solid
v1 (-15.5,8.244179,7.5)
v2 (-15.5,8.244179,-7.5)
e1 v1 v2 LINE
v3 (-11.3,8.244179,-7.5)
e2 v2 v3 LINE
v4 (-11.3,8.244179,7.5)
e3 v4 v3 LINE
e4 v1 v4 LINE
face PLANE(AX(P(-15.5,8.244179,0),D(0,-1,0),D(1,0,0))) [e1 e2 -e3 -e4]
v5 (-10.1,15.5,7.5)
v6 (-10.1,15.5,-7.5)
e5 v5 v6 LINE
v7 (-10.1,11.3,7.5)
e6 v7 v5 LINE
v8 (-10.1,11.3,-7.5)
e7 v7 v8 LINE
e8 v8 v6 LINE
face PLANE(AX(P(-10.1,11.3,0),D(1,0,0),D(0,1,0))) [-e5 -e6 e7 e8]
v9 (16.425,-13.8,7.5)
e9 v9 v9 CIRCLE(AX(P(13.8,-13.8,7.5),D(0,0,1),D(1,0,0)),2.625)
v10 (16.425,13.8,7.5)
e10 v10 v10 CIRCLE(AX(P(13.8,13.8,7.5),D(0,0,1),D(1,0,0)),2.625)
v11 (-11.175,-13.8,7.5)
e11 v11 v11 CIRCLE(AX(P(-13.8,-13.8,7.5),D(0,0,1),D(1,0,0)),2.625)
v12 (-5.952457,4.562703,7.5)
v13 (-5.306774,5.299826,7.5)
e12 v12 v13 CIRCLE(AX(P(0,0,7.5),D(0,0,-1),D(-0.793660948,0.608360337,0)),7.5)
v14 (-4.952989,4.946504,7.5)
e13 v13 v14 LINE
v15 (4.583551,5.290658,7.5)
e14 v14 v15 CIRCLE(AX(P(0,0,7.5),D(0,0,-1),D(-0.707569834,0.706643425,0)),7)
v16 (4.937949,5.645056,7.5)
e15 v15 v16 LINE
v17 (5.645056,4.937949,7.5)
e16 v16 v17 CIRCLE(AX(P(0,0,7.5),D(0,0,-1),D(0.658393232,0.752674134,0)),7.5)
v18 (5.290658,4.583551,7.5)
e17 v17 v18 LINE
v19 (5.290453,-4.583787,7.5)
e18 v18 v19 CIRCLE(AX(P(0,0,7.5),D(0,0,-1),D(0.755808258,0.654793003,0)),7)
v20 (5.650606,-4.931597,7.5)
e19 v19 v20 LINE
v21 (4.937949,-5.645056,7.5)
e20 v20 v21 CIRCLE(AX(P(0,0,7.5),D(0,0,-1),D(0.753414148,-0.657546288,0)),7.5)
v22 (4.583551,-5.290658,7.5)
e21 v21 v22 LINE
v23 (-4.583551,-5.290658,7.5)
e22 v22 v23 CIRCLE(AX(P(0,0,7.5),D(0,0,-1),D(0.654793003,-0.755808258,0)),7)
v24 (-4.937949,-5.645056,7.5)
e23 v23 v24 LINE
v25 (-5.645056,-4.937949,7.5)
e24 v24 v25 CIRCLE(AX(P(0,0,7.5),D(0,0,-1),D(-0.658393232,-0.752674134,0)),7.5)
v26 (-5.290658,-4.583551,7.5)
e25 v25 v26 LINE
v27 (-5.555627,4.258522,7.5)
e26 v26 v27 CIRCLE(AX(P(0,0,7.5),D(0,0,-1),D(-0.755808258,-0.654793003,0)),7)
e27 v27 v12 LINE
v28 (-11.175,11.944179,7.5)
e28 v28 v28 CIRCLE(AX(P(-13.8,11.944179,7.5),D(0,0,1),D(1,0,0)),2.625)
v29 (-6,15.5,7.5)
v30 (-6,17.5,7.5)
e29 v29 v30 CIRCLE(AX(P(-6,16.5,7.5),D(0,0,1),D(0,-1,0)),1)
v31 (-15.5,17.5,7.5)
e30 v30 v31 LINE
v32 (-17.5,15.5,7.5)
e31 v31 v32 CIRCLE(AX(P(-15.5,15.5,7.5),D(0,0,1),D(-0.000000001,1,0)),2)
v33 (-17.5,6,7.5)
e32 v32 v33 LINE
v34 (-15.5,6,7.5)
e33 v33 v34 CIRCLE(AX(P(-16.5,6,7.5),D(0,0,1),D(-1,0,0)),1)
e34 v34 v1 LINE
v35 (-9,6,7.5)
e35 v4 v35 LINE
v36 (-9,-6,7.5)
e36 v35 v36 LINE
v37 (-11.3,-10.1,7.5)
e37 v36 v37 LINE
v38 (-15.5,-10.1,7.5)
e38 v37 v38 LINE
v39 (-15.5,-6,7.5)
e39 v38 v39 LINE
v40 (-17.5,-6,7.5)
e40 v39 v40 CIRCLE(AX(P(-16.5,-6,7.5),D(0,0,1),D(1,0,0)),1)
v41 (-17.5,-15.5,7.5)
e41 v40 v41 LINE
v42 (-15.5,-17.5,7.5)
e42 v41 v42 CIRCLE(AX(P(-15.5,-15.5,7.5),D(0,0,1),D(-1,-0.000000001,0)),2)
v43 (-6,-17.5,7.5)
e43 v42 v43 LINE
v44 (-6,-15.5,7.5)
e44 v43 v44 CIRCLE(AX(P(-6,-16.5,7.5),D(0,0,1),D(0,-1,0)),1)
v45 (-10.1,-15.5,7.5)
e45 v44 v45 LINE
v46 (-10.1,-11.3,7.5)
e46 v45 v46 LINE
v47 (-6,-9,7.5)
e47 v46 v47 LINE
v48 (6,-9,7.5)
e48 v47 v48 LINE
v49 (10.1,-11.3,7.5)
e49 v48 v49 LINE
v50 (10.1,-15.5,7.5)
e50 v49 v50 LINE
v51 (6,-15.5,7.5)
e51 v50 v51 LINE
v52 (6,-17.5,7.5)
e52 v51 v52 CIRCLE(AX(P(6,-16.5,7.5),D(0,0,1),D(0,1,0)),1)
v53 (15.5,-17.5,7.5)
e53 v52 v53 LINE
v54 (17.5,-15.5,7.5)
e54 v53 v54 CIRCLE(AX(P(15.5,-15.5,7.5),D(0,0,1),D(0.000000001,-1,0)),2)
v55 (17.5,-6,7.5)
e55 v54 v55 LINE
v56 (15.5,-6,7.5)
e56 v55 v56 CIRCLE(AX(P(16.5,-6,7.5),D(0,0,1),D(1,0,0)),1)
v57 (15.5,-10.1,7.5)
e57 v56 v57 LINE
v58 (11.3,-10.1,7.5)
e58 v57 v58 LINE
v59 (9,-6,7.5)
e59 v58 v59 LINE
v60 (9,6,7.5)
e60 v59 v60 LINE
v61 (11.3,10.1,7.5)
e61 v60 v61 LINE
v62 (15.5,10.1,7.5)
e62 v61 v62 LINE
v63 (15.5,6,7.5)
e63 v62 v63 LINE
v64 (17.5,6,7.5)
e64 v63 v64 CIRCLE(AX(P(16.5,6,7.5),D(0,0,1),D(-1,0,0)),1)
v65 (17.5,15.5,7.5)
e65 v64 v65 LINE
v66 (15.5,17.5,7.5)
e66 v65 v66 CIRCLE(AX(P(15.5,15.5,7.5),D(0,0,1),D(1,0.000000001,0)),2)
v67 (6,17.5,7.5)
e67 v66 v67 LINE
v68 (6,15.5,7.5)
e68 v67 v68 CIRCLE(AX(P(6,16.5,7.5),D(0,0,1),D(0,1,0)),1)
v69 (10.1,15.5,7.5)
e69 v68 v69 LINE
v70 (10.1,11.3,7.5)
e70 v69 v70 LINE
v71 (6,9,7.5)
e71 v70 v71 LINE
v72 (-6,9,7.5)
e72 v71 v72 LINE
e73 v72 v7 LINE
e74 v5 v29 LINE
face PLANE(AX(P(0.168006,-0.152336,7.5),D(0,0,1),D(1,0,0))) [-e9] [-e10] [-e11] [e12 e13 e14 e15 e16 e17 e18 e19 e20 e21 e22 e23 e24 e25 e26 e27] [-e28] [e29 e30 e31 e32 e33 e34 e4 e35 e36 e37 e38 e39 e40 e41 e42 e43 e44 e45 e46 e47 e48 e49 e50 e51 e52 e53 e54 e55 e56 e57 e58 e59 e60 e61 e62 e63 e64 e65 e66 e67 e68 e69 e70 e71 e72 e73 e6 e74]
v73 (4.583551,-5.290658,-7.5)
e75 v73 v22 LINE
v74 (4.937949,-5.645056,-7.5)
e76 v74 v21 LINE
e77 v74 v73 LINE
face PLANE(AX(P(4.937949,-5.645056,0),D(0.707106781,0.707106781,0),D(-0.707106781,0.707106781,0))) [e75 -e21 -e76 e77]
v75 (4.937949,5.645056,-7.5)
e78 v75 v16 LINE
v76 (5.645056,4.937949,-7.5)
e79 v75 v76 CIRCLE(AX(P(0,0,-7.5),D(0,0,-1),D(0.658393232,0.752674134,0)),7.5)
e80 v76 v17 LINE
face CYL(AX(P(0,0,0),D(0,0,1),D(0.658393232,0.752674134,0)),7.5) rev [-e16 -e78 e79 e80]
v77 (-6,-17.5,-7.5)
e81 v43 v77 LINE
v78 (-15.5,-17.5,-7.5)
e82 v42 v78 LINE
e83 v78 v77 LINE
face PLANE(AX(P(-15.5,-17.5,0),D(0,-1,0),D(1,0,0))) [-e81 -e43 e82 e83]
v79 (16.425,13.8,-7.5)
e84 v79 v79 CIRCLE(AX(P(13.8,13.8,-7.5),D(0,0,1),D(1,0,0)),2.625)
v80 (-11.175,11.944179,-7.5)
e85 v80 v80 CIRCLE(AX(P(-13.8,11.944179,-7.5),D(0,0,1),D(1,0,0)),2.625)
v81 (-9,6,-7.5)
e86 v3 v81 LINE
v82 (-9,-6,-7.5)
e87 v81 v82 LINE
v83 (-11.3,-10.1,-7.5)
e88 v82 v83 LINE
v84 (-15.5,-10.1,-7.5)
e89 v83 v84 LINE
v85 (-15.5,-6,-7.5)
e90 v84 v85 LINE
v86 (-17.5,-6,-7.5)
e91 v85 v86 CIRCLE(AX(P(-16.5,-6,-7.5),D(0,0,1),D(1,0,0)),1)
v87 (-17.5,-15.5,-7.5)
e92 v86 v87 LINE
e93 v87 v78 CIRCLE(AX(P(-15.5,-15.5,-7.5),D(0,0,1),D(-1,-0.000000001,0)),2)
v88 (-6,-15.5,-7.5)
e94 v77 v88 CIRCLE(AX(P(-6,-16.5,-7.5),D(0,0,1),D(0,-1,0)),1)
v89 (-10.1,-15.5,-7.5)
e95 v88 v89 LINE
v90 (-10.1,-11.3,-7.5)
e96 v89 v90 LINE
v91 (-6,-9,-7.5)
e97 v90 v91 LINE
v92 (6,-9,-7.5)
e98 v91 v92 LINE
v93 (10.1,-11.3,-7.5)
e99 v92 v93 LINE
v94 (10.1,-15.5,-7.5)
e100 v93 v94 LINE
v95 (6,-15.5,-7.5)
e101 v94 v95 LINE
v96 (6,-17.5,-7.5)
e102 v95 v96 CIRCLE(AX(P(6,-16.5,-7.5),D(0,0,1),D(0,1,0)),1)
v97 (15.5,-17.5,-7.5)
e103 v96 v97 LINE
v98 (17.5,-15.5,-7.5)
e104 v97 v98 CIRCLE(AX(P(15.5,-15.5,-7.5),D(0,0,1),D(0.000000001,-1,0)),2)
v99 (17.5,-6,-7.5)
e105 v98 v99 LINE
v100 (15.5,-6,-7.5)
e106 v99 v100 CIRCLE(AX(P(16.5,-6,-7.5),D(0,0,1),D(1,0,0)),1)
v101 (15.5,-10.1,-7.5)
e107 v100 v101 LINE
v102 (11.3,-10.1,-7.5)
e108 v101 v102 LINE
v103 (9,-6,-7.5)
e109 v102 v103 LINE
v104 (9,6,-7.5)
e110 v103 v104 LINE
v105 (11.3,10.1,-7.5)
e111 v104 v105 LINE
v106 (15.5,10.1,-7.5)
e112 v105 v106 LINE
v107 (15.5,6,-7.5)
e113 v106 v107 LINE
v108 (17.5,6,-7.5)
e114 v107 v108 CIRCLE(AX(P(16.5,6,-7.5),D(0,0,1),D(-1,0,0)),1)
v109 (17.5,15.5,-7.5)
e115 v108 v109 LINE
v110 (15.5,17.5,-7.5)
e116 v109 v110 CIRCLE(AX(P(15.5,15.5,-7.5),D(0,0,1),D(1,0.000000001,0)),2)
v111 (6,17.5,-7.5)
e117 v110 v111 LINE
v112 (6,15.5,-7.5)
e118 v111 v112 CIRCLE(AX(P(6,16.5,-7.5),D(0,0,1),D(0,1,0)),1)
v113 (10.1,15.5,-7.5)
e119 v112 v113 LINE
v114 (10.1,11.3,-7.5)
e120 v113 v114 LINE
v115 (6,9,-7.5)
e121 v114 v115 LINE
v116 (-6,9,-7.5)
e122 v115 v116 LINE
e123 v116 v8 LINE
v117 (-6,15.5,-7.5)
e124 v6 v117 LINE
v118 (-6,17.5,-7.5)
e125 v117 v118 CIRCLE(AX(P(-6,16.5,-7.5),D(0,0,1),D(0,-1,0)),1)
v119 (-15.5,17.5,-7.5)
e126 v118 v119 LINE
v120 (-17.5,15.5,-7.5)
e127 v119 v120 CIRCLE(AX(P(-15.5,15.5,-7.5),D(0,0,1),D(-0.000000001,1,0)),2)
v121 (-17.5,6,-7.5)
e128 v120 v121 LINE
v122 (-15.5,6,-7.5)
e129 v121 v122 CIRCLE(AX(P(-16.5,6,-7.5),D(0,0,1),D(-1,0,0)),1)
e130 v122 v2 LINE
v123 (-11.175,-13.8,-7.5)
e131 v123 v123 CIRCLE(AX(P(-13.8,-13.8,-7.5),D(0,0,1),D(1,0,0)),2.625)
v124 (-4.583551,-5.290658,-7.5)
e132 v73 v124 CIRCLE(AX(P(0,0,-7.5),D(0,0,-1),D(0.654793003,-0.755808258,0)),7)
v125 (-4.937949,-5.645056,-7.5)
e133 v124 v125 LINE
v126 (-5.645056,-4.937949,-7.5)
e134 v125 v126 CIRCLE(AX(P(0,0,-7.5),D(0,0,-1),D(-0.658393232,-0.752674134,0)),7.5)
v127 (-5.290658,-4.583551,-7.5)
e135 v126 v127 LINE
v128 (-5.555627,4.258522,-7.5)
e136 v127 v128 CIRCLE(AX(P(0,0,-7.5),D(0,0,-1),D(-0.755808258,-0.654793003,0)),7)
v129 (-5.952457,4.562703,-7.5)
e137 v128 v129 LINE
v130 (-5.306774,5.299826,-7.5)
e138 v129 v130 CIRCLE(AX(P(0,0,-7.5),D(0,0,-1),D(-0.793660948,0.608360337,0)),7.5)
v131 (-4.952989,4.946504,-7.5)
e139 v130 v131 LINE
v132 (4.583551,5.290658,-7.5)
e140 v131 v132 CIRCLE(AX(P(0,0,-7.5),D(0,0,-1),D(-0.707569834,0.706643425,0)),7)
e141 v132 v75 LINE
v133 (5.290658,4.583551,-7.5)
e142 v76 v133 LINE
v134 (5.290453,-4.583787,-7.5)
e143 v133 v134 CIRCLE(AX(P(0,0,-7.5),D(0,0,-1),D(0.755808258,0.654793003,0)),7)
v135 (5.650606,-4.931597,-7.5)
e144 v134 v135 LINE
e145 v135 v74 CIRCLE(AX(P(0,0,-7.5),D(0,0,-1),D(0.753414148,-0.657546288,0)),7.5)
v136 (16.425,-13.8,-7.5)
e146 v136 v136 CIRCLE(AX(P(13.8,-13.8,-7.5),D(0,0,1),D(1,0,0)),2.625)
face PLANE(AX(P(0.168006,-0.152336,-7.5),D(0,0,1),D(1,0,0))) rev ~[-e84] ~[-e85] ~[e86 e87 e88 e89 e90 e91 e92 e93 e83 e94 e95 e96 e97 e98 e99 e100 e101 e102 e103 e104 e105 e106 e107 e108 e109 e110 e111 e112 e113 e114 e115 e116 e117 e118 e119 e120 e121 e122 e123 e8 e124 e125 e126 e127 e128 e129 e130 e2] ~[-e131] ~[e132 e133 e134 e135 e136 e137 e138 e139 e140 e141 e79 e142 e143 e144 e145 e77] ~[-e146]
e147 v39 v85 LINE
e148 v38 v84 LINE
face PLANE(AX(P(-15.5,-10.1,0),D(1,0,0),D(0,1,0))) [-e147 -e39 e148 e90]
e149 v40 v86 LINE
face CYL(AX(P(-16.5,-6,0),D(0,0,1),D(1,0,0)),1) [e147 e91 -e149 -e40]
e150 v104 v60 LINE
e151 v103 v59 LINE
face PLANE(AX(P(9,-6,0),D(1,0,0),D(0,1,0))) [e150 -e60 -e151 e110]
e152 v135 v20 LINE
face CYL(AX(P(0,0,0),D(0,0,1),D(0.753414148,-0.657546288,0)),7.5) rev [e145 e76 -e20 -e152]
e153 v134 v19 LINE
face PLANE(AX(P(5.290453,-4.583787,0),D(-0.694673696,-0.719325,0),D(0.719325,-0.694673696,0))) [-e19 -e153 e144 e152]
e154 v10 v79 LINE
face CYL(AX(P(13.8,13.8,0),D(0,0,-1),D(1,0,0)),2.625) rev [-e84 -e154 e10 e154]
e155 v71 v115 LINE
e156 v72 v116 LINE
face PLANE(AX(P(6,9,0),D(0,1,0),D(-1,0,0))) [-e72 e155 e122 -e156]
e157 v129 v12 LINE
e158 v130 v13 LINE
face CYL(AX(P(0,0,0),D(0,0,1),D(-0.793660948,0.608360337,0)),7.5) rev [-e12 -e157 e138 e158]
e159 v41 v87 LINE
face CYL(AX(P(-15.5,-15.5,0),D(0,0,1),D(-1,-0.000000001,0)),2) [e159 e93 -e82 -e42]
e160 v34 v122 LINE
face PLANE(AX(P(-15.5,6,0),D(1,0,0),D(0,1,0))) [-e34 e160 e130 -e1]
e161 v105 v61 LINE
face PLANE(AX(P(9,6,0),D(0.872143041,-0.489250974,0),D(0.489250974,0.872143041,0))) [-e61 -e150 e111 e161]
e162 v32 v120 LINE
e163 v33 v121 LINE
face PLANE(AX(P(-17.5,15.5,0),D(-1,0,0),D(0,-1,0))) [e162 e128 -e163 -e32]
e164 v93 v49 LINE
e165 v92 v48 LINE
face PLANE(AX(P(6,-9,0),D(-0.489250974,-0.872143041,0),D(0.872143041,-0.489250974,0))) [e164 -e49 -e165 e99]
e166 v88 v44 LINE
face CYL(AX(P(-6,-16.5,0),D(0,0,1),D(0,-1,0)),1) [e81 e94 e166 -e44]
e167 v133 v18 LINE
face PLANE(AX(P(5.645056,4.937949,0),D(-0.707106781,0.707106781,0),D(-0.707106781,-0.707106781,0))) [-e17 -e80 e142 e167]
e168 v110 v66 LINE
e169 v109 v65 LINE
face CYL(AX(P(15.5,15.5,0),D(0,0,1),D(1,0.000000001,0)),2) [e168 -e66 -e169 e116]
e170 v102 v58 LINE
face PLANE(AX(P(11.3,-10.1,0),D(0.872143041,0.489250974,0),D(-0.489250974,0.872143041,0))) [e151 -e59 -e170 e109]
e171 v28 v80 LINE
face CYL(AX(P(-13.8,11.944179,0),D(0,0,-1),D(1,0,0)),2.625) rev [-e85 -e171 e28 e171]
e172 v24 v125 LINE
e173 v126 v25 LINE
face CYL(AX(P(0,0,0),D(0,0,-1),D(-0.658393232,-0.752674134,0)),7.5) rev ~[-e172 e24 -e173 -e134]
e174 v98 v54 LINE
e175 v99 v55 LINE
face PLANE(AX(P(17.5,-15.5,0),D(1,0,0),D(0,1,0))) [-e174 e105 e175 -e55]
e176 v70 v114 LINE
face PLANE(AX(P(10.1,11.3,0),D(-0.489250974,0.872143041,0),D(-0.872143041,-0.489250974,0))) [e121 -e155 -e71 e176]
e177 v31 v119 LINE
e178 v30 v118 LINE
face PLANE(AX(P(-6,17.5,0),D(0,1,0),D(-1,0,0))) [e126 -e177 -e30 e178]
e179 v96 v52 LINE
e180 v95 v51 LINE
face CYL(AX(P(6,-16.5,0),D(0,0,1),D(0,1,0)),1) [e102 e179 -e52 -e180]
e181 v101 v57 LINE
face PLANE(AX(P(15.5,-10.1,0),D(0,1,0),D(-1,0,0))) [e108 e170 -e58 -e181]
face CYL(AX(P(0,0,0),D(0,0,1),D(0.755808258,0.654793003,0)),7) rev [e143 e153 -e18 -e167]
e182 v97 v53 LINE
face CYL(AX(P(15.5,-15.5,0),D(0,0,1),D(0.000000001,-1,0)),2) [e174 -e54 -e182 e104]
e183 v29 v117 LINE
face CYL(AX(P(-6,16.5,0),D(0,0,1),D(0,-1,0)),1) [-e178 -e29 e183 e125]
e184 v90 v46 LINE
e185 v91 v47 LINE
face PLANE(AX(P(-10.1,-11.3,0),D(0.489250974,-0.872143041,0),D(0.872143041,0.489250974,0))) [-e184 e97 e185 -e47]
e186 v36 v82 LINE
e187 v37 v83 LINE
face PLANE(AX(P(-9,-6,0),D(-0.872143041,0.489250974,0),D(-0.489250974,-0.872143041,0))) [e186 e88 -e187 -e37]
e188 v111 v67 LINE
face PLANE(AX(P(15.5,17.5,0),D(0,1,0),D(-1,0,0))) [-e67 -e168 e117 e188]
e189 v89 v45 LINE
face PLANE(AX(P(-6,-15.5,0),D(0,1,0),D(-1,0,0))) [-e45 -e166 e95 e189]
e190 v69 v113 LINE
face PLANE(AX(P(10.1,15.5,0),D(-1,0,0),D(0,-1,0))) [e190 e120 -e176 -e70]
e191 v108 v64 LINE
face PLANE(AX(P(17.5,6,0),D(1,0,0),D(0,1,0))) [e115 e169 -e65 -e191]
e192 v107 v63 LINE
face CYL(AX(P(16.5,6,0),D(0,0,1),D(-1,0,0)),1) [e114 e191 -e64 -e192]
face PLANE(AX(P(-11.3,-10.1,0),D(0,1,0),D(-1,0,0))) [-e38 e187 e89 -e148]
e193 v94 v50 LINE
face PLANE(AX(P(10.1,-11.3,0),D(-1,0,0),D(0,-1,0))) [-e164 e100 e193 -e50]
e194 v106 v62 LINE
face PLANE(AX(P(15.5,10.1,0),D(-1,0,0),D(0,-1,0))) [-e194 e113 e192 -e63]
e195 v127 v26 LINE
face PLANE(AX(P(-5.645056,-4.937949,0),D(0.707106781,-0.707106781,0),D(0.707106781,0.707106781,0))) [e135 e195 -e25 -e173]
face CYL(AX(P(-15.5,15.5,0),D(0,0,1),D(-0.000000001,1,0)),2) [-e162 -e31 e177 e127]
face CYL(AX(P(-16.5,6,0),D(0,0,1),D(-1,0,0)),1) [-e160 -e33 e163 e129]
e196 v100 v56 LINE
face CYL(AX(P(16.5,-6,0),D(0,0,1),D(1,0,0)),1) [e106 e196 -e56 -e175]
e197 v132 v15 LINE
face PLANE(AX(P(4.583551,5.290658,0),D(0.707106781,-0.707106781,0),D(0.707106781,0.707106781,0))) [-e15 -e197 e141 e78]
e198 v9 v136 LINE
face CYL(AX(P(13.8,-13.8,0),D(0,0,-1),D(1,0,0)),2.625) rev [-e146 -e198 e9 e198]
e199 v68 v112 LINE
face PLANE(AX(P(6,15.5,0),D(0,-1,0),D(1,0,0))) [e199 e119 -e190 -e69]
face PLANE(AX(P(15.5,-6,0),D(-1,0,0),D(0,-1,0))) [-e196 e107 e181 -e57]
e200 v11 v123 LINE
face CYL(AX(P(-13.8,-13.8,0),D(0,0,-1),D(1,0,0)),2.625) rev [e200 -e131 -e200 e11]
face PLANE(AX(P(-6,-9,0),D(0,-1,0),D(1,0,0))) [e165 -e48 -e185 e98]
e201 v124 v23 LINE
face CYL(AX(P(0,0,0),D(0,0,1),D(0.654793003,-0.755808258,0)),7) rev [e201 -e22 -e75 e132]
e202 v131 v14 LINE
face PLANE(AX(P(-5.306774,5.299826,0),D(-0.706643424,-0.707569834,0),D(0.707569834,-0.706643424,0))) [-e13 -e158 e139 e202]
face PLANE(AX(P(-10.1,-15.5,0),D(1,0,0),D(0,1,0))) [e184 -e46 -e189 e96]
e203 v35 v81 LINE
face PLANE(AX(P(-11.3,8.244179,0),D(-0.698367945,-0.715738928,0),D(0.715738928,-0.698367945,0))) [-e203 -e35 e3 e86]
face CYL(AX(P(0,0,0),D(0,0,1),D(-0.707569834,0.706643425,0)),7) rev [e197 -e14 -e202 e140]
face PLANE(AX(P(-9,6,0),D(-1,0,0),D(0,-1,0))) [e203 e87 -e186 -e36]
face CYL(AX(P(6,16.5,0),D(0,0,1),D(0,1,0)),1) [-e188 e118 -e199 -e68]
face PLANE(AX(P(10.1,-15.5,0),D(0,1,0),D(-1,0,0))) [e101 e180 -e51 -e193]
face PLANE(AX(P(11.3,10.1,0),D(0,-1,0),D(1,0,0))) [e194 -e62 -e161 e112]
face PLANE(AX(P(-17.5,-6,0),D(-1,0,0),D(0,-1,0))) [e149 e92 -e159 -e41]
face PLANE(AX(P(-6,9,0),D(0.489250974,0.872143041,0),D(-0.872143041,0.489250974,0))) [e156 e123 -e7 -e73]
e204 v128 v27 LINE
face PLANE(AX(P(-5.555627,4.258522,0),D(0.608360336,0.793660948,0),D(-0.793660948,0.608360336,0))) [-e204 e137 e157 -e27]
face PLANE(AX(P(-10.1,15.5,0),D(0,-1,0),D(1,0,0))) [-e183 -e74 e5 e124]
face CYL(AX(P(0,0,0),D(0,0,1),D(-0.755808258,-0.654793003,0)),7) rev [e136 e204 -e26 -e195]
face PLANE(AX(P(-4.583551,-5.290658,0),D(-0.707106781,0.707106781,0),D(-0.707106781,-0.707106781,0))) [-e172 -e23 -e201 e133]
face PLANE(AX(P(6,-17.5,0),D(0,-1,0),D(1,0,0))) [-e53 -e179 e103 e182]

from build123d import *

# Parameters (mm, degrees)
PROFILE_SECTION_35X35_R     = 2.625
PROFILE_EXTRUSION_L15_DEPTH = 7.5


with BuildPart() as part:
    # Profile Section 35x35 → Profile Extrusion L15 (new, symmetric)
    with BuildSketch(Plane.XY):
        with BuildLine():
            Line((-13.8, -17.5), (-6, -17.5))
            ThreePointArc((-6, -17.5), (-5, -16.5), (-6, -15.5))
            Line((-6, -15.5), (-10.1, -15.5))
            Line((-10.1, -15.5), (-10.1, -11.3))
            Line((-10.1, -11.3), (-6, -9))
            Line((-6, -9), (0, -9))
            Line((0, -9), (6, -9))
            Line((6, -9), (10.1, -11.3))
            Line((10.1, -11.3), (10.1, -15.5))
            Line((10.1, -15.5), (6, -15.5))
            ThreePointArc((6, -15.5), (5, -16.5), (6, -17.5))
            Line((6, -17.5), (13.8, -17.5))
            Line((13.8, -17.5), (15.5, -17.5))
            ThreePointArc((15.5, -17.5), (16.914213562, -16.914213562), (17.5, -15.5))
            Line((17.5, -15.5), (17.5, -6))
            ThreePointArc((17.5, -6), (16.5, -5), (15.5, -6))
            Line((15.5, -6), (15.5, -10.1))
            Line((15.5, -10.1), (11.3, -10.1))
            Line((11.3, -10.1), (9, -6))
            Line((9, -6), (9, 0))
            Line((9, 0), (9, 6))
            Line((9, 6), (11.3, 10.1))
            Line((11.3, 10.1), (15.5, 10.1))
            Line((15.5, 10.1), (15.5, 6))
            ThreePointArc((15.5, 6), (16.5, 5), (17.5, 6))
            Line((17.5, 6), (17.5, 15.5))
            ThreePointArc((17.5, 15.5), (16.914213562, 16.914213562), (15.5, 17.5))
            Line((15.5, 17.5), (13.8, 17.5))
            Line((13.8, 17.5), (6, 17.5))
            ThreePointArc((6, 17.5), (5, 16.5), (6, 15.5))
            Line((6, 15.5), (10.1, 15.5))
            Line((10.1, 15.5), (10.1, 11.3))
            Line((10.1, 11.3), (6, 9))
            Line((6, 9), (0, 9))
            Line((0, 9), (-6, 9))
            Line((-6, 9), (-10.1, 11.3))
            Line((-10.1, 11.3), (-10.1, 15.5))
            Line((-10.1, 15.5), (-6, 15.5))
            ThreePointArc((-6, 15.5), (-5, 16.5), (-6, 17.5))
            Line((-6, 17.5), (-13.8, 17.5))
            Line((-13.8, 17.5), (-15.5, 17.5))
            ThreePointArc((-15.5, 17.5), (-16.914213562, 16.914213562), (-17.5, 15.5))
            Line((-17.5, 15.5), (-17.5, 6))
            ThreePointArc((-17.5, 6), (-16.5, 5), (-15.5, 6))
            Line((-15.5, 6), (-15.5, 8.244179001))
            Line((-15.5, 8.244179001), (-11.3, 8.244179001))
            Line((-11.3, 8.244179001), (-9, 6))
            Line((-9, 6), (-9, 0))
            Line((-9, 0), (-9, -6))
            Line((-9, -6), (-11.3, -10.1))
            Line((-11.3, -10.1), (-15.5, -10.1))
            Line((-15.5, -10.1), (-15.5, -6))
            ThreePointArc((-15.5, -6), (-16.5, -5), (-17.5, -6))
            Line((-17.5, -6), (-17.5, -15.5))
            ThreePointArc((-17.5, -15.5), (-16.914213562, -16.914213562), (-15.5, -17.5))
            Line((-15.5, -17.5), (-13.8, -17.5))
        make_face()
        with Locations((-13.8, -13.8)):
            Circle(PROFILE_SECTION_35X35_R, mode=Mode.SUBTRACT)
        with Locations((13.8, -13.8)):
            Circle(PROFILE_SECTION_35X35_R, mode=Mode.SUBTRACT)
        with Locations((-13.8, 11.944179001)):
            Circle(PROFILE_SECTION_35X35_R, mode=Mode.SUBTRACT)
        with BuildLine():
            Line((5.645056013, 4.937949232), (5.290657805, 4.583551024))
            ThreePointArc((5.290657805, 4.583551024), (6.999999998, -0.000156062), (5.290453424, -4.583786925))
            Line((5.290453424, -4.583786925), (5.650606112, -4.931597162))
            ThreePointArc((5.650606112, -4.931597162), (5.30628231, -5.300317731), (4.937949232, -5.645056013))
            Line((4.937949232, -5.645056013), (4.583551024, -5.290657805))
            ThreePointArc((4.583551024, -5.290657805), (0, -7), (-4.583551024, -5.290657805))
            Line((-4.583551024, -5.290657805), (-4.937949232, -5.645056013))
            ThreePointArc((-4.937949232, -5.645056013), (-5.303300859, -5.303300859), (-5.645056013, -4.937949232))
            Line((-5.645056013, -4.937949232), (-5.290657805, -4.583551024))
            ThreePointArc((-5.290657805, -4.583551024), (-6.996859079, -0.209673625), (-5.555626638, 4.258522357))
            Line((-5.555626638, 4.258522357), (-5.952457112, 4.562702525))
            ThreePointArc((-5.952457112, 4.562702525), (-5.64166709, 4.941820762), (-5.306773753, 5.299825689))
            Line((-5.306773753, 5.299825689), (-4.952988836, 4.946503977))
            ThreePointArc((-4.952988836, 4.946503977), (-0.252451062, 6.995446266), (4.583551024, 5.290657805))
            Line((4.583551024, 5.290657805), (4.937949232, 5.645056013))
            ThreePointArc((4.937949232, 5.645056013), (5.303300859, 5.303300859), (5.645056013, 4.937949232))
        make_face(mode=Mode.SUBTRACT)
        with Locations((13.8, 13.8)):
            Circle(PROFILE_SECTION_35X35_R, mode=Mode.SUBTRACT)
    extrude(amount=PROFILE_EXTRUSION_L15_DEPTH, both=True)


solid = part.part
